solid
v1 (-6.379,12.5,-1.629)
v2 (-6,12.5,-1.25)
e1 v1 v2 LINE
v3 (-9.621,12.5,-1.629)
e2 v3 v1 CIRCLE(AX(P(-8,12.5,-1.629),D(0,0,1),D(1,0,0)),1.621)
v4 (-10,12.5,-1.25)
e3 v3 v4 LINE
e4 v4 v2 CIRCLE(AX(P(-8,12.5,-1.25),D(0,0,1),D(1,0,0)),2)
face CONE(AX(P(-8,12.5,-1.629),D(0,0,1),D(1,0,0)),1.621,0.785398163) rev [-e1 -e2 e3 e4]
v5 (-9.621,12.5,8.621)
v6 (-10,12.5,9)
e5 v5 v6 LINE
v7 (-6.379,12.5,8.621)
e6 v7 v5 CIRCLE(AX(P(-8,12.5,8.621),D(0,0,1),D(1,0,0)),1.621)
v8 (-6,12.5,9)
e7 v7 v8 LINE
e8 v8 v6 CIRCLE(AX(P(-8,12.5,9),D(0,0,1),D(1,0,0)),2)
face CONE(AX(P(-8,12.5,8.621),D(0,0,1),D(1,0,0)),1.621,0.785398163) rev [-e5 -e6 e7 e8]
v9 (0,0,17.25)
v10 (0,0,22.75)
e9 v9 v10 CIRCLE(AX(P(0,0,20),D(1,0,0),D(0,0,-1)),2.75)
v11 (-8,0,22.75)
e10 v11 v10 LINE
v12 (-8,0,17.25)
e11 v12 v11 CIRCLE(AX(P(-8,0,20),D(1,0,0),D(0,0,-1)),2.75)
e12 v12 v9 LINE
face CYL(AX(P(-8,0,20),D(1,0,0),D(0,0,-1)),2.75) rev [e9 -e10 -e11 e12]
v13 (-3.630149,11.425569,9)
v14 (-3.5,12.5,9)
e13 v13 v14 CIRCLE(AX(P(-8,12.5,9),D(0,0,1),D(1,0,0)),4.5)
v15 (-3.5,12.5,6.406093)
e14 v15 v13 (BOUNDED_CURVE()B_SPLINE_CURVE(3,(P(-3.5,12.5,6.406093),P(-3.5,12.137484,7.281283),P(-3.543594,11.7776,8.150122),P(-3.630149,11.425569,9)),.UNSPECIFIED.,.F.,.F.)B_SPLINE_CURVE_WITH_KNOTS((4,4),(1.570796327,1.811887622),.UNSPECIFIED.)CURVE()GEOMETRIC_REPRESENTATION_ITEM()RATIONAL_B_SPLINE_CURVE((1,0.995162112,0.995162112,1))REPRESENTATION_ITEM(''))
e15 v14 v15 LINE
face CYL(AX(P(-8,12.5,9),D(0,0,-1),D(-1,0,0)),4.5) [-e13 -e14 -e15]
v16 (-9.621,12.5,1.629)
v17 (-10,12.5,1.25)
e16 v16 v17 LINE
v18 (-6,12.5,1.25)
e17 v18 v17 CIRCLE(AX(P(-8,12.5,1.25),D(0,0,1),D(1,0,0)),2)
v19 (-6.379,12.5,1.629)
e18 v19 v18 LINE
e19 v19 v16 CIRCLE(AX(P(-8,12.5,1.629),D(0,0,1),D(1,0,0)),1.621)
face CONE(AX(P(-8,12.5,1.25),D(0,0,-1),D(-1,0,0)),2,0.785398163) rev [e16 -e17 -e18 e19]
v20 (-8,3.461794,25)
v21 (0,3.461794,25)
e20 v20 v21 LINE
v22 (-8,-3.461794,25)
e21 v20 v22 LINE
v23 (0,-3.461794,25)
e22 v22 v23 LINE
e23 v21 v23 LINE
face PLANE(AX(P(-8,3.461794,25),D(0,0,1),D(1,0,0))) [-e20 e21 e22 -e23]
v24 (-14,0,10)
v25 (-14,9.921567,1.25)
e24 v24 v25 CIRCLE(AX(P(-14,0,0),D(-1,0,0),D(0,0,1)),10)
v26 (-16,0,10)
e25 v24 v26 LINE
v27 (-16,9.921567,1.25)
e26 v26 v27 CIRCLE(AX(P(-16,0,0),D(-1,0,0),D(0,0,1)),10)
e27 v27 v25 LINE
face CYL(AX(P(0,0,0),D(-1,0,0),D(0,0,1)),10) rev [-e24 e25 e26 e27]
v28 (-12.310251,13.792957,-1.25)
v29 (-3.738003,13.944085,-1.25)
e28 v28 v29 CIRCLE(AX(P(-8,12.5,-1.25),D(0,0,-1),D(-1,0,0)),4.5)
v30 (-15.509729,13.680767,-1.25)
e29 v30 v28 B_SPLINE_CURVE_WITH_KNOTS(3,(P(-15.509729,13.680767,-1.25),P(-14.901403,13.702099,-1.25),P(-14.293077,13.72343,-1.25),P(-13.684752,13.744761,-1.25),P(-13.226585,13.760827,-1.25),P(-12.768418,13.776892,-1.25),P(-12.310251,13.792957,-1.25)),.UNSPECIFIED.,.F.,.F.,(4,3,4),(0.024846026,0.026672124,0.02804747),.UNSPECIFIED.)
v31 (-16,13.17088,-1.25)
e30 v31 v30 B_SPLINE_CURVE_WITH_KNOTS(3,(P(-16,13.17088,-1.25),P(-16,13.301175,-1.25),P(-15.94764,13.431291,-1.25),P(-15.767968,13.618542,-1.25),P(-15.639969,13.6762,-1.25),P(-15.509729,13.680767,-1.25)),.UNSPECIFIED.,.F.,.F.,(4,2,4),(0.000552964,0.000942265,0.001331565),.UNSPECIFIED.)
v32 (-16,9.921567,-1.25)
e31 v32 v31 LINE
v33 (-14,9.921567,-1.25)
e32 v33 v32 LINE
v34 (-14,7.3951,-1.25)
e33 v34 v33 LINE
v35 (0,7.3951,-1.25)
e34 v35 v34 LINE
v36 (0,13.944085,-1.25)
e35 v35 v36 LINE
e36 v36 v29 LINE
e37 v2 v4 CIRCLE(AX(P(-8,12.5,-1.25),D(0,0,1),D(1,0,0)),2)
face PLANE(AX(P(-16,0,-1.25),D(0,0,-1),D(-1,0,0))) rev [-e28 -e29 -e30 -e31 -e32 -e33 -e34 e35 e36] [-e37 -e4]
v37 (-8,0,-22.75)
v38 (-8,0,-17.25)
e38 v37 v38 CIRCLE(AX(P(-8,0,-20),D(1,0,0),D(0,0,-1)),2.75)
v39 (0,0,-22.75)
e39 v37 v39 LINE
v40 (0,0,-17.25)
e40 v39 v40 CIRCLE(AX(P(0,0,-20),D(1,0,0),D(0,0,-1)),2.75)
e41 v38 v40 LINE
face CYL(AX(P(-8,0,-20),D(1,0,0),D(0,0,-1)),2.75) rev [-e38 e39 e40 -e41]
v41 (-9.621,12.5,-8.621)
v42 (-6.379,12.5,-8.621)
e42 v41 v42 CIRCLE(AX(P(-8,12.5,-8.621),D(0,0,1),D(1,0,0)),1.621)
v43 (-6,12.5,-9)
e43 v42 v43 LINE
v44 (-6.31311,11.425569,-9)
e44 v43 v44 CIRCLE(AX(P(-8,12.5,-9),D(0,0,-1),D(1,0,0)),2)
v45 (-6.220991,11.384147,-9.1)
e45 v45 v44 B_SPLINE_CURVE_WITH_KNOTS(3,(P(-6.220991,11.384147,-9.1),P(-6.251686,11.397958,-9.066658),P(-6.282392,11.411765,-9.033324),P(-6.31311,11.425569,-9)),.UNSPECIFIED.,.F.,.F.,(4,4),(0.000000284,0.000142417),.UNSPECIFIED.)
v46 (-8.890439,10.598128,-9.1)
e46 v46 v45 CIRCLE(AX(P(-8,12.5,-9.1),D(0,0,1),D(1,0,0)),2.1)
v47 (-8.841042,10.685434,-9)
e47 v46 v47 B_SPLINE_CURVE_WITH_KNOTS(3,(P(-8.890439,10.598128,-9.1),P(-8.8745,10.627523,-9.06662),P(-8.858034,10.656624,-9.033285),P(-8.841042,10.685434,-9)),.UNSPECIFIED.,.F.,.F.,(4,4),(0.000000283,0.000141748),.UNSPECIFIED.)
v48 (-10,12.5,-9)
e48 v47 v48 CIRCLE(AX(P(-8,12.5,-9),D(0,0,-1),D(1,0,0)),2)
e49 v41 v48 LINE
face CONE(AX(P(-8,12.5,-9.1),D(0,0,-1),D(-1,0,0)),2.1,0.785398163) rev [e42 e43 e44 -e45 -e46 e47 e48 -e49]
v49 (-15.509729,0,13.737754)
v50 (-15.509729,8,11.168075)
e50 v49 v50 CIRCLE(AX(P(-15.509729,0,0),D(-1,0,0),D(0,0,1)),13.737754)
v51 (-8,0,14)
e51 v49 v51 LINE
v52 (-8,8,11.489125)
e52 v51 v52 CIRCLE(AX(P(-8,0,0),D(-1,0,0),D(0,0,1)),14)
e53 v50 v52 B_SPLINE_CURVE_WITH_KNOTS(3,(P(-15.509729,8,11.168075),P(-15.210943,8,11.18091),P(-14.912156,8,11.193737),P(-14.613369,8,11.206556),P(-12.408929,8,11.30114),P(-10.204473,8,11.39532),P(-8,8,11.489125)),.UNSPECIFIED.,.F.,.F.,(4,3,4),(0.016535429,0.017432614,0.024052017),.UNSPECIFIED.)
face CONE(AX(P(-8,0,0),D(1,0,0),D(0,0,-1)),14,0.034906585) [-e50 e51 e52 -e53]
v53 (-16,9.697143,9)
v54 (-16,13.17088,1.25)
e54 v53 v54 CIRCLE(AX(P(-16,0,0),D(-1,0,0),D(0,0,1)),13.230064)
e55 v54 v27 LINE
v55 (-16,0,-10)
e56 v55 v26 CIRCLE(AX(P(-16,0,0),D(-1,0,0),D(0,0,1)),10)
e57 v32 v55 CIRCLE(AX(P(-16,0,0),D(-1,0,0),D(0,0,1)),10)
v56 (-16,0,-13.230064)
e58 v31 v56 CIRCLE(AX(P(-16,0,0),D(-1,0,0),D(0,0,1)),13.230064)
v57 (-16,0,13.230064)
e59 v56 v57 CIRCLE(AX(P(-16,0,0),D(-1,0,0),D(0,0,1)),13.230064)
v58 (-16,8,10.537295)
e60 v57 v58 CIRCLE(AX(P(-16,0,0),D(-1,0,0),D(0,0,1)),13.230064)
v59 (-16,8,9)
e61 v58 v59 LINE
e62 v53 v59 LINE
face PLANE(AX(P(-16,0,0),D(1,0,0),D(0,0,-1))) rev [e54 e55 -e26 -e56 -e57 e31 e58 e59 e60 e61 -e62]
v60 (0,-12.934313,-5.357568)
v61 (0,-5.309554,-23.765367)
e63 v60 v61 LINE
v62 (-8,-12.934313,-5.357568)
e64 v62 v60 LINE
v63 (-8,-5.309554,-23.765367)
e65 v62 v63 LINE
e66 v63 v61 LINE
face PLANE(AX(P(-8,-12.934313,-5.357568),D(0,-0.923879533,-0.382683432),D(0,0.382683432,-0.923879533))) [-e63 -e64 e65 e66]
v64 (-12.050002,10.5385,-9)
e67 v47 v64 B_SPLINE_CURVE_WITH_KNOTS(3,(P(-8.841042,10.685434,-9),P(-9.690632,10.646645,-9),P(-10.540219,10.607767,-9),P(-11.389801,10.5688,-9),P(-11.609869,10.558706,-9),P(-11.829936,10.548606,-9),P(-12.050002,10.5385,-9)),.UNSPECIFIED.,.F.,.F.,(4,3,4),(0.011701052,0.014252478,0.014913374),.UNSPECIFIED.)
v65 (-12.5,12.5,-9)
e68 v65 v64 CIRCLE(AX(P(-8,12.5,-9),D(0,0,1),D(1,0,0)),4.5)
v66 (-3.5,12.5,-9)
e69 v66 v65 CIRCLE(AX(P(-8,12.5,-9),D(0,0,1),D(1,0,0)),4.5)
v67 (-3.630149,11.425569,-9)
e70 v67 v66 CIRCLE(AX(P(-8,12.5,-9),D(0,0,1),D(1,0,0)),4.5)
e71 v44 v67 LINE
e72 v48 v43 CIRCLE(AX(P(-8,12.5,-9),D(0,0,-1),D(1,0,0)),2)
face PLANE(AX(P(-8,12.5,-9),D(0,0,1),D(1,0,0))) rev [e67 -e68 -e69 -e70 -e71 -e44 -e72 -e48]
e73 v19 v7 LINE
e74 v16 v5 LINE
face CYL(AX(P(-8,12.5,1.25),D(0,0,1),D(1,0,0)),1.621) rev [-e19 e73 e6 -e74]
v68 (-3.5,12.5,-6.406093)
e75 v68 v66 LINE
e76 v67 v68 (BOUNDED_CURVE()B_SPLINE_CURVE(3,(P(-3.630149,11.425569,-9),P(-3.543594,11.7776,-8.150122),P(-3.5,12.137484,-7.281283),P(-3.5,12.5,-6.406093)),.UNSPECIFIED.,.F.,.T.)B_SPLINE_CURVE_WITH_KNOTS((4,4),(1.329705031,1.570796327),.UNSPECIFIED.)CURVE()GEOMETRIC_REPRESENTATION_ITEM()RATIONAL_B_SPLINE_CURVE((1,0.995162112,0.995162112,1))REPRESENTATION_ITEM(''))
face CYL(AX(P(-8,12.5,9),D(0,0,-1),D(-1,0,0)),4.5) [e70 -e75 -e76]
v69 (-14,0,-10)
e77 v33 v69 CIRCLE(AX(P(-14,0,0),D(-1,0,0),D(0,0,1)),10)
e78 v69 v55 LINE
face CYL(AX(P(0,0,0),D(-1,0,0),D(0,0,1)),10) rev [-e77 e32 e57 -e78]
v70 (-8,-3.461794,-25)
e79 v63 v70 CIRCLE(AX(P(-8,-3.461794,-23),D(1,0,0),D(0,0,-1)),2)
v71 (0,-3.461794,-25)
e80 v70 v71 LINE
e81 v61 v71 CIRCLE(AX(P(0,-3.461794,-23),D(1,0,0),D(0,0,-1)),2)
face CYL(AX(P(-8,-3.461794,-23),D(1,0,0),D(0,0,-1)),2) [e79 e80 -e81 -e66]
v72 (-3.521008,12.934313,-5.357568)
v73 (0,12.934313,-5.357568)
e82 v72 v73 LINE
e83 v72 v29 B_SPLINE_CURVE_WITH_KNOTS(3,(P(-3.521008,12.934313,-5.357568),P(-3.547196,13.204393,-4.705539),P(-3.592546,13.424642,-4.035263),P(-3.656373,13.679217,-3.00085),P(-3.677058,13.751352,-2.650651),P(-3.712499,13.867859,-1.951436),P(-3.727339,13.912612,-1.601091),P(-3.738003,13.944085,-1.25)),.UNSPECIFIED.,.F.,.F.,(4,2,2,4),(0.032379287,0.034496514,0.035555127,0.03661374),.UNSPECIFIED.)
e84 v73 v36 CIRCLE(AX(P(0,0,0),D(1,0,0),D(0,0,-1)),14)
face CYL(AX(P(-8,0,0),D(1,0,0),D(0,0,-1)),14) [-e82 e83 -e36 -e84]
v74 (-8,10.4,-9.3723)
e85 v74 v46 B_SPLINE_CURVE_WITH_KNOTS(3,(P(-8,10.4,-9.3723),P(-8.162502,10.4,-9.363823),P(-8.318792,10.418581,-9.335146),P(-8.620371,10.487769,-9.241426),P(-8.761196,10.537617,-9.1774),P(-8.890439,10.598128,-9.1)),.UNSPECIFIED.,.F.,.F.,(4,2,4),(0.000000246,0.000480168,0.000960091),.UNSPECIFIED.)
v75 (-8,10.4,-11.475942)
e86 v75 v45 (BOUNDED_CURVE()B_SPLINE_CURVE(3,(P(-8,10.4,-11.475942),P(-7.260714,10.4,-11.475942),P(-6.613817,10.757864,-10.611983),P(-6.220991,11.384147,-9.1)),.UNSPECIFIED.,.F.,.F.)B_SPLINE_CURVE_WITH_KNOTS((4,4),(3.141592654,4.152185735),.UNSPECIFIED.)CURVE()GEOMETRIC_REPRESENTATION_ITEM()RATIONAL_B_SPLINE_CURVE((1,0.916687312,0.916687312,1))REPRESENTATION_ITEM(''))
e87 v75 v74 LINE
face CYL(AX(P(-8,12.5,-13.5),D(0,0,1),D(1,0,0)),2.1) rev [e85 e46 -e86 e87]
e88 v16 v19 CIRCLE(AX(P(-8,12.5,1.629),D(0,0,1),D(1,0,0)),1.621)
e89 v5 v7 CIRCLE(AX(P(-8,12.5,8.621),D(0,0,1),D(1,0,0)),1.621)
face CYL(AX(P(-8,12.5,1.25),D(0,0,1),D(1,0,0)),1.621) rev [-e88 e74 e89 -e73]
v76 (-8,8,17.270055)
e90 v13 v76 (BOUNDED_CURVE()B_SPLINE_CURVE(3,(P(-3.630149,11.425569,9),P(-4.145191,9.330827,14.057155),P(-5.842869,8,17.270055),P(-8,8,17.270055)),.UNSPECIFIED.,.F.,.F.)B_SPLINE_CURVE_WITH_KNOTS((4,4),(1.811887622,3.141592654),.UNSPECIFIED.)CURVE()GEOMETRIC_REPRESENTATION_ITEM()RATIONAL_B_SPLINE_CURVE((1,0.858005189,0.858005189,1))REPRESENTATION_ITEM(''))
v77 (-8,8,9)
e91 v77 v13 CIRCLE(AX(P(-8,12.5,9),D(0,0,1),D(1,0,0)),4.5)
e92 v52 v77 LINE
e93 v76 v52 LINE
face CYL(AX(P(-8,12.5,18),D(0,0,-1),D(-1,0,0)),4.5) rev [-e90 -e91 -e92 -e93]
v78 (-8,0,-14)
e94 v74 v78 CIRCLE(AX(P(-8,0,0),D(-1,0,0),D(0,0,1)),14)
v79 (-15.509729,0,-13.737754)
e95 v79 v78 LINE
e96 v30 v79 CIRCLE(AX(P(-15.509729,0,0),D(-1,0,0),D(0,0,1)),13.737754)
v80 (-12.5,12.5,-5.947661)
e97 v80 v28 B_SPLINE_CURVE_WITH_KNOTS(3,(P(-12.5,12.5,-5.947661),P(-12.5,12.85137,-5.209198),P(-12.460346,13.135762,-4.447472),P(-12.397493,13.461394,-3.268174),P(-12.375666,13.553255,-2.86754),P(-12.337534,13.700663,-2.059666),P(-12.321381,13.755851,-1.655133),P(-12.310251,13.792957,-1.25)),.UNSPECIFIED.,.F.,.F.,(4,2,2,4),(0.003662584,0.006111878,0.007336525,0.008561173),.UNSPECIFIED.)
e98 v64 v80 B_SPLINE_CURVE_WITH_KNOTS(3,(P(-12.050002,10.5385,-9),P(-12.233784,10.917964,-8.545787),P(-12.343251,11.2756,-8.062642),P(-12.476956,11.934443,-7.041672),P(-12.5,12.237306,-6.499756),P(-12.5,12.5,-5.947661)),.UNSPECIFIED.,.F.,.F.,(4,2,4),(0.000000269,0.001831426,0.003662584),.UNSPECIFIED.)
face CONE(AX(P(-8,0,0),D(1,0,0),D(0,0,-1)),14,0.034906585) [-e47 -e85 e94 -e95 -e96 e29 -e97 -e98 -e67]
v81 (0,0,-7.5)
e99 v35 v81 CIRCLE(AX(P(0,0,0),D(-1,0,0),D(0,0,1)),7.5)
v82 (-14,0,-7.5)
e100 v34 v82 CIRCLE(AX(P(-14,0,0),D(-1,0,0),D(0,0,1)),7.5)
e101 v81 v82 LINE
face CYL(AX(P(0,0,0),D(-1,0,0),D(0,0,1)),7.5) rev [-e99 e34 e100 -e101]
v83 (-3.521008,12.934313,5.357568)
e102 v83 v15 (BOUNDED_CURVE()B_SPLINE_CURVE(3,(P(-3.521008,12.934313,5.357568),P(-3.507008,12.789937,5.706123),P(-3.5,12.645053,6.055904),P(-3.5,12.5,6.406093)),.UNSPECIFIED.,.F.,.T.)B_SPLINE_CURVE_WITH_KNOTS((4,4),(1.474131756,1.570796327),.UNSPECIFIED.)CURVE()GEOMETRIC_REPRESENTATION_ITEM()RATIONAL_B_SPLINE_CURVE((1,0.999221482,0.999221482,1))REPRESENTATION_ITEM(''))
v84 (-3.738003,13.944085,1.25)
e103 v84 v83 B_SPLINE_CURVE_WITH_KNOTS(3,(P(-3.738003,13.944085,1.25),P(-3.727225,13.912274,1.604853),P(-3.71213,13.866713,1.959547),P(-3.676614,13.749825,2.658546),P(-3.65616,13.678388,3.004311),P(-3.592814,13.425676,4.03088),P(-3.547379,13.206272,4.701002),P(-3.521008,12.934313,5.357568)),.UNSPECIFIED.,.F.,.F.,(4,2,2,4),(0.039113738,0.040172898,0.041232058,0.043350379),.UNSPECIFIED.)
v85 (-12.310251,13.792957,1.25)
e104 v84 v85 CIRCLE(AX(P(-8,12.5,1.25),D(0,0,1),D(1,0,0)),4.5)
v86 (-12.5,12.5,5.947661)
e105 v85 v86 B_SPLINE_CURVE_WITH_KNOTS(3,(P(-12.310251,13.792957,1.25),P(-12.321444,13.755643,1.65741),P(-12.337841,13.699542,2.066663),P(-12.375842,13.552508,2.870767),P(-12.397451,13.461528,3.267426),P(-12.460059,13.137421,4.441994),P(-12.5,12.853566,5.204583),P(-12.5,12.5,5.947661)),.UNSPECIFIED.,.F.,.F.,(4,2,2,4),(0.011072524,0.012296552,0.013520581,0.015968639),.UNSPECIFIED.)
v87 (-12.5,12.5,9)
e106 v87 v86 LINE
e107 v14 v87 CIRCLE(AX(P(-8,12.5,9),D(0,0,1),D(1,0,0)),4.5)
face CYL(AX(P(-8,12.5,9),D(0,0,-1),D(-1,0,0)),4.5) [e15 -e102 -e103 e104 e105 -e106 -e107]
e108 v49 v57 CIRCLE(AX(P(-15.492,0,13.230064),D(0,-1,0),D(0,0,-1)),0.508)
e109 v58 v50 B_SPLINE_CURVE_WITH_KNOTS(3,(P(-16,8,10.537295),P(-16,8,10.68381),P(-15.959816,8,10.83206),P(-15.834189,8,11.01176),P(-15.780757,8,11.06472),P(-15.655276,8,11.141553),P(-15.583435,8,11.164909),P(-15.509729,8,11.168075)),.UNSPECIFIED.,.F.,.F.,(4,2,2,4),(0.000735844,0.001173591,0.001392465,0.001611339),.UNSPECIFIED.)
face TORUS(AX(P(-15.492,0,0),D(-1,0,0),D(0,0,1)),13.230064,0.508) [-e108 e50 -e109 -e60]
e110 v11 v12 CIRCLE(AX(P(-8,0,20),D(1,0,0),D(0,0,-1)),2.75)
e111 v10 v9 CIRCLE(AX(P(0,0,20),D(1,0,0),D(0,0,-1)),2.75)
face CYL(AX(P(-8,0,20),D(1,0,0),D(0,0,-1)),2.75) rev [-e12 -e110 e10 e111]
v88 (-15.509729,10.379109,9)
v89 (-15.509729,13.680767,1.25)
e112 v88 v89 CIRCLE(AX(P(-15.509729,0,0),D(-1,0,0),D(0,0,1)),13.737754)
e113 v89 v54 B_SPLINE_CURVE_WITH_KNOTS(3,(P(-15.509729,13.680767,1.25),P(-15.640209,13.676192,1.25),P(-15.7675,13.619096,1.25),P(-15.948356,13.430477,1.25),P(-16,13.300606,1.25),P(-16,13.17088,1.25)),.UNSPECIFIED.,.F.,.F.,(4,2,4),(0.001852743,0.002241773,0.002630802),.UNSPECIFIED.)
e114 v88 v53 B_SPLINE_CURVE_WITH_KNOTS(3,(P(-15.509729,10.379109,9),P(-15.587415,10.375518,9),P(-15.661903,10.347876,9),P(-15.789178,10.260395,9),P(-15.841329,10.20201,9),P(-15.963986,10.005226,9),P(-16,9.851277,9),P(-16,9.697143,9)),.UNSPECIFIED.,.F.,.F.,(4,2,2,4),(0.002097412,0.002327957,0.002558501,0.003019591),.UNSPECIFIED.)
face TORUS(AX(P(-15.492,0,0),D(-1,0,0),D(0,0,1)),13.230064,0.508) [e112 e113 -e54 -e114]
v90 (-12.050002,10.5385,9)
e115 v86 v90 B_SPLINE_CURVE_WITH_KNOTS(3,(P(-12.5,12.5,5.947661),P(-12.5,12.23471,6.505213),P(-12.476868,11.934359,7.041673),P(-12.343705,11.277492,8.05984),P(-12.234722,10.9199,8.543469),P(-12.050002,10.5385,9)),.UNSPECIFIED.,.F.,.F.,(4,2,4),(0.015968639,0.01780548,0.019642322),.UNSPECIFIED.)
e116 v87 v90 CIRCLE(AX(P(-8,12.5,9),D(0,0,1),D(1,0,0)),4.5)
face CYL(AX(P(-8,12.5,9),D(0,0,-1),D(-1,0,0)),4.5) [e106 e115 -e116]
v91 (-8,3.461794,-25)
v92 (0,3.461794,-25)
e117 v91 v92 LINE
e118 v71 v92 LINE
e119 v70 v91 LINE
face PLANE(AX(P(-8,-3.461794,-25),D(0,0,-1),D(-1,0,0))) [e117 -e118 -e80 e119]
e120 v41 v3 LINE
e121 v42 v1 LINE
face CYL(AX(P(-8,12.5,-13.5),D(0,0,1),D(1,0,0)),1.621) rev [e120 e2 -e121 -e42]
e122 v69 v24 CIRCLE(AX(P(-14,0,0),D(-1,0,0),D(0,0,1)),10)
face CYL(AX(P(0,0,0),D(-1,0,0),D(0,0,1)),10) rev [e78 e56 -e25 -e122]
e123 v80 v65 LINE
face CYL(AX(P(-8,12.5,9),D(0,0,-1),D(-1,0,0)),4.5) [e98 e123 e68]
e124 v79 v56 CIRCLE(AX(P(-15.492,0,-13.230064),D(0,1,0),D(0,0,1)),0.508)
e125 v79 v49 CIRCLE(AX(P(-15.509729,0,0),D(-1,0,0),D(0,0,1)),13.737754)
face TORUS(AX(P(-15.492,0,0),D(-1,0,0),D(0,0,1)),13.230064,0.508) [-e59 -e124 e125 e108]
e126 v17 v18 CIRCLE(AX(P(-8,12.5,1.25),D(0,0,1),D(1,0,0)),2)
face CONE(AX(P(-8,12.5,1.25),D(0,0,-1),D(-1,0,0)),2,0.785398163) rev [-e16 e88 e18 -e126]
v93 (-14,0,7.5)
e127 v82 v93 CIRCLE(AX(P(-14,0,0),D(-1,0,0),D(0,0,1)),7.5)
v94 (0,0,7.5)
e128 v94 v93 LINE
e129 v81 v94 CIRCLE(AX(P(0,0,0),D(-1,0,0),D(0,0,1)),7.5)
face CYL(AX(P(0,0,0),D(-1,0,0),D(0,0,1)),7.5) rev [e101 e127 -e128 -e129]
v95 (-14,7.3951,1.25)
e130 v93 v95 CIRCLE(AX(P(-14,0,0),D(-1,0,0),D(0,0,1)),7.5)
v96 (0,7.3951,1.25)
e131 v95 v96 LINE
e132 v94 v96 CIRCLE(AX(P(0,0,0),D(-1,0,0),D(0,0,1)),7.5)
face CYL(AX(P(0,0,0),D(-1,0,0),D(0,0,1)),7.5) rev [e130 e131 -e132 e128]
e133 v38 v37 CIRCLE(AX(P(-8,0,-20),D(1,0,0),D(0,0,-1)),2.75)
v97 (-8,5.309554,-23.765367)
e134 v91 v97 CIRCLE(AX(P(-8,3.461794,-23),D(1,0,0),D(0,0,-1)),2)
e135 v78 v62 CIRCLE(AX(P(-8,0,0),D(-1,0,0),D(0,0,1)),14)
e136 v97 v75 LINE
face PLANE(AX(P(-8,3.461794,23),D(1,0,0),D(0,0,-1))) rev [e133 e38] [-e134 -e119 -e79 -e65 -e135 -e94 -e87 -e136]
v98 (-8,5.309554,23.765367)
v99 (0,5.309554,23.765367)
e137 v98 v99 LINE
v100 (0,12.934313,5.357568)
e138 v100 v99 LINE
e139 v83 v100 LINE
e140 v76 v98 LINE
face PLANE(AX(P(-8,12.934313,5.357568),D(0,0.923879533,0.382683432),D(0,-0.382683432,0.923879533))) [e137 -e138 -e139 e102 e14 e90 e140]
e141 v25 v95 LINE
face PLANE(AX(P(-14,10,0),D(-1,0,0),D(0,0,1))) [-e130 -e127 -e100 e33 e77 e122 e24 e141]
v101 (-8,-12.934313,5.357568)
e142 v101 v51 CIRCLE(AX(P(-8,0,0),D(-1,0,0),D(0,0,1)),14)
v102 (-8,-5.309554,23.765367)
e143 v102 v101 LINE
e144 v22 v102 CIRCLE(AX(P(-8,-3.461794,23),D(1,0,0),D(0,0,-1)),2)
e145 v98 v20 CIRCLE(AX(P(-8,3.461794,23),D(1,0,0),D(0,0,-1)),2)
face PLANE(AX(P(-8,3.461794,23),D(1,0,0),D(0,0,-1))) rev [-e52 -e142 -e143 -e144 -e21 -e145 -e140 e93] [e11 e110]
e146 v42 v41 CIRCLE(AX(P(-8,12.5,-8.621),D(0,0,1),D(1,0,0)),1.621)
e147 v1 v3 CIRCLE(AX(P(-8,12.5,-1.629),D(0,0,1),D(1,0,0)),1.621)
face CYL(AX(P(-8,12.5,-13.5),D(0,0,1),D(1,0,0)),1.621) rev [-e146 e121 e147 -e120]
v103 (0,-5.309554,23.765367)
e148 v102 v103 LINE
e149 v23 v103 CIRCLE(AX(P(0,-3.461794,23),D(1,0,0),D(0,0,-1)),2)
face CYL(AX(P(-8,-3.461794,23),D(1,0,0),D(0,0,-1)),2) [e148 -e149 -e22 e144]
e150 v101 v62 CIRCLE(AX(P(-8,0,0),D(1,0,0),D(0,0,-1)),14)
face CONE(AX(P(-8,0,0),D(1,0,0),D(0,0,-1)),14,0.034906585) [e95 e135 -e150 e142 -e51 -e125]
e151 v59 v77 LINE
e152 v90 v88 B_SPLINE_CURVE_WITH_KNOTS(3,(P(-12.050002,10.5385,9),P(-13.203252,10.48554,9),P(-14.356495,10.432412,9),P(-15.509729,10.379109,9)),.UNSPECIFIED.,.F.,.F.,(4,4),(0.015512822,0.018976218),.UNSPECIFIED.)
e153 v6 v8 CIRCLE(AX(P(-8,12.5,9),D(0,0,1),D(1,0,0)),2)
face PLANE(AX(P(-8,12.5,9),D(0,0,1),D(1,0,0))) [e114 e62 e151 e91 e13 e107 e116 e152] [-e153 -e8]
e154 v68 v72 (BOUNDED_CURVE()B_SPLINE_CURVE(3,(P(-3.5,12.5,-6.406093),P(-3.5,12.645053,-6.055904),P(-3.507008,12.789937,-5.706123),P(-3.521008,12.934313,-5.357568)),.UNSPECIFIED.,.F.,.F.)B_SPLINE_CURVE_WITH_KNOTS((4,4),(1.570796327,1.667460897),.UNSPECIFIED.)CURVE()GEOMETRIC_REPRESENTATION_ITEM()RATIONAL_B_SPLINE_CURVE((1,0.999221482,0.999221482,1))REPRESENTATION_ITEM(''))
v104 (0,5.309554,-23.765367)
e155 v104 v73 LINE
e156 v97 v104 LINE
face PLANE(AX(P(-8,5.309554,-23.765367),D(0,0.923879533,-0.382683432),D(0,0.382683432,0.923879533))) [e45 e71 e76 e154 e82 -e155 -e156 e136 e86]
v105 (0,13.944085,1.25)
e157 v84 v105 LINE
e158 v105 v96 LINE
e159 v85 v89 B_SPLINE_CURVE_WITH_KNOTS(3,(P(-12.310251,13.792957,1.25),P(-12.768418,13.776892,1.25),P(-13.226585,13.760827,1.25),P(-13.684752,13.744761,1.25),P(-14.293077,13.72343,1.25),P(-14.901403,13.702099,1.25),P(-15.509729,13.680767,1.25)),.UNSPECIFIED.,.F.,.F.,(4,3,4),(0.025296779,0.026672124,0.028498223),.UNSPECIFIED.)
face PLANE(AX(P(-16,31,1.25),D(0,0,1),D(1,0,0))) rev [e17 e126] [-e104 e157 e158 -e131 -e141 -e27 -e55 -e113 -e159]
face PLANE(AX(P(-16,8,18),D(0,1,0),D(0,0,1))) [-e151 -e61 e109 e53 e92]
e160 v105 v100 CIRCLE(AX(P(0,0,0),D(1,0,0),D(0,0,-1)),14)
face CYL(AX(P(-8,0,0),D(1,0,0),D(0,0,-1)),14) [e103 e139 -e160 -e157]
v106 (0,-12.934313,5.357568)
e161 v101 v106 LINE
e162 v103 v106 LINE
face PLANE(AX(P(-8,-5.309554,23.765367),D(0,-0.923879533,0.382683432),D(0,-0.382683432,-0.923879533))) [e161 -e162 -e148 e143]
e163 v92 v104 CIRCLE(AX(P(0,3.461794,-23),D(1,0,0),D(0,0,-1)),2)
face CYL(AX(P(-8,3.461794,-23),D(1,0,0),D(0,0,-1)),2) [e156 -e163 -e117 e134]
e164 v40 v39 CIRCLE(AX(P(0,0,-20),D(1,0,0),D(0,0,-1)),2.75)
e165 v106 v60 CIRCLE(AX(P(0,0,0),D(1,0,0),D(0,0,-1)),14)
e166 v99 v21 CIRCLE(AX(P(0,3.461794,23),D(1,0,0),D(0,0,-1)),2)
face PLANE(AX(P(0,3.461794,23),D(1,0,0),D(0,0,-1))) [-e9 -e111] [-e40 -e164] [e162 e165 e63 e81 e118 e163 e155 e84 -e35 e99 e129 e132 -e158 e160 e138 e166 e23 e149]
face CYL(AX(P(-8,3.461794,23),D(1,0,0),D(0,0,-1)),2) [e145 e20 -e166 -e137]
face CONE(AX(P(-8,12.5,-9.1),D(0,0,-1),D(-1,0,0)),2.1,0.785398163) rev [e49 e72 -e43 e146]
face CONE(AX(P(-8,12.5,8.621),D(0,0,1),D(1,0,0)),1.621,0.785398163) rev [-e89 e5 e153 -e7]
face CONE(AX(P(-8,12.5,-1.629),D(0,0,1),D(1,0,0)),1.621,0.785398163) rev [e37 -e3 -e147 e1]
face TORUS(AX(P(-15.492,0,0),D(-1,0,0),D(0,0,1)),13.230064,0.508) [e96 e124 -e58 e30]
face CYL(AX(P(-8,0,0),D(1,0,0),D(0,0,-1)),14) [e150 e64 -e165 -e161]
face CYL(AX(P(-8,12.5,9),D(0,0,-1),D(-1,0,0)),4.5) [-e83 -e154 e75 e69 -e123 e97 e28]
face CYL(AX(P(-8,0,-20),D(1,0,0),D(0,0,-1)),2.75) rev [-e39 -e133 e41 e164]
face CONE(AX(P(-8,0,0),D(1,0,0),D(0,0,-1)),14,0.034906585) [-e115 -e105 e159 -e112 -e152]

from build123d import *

# Parameters (mm, degrees)
EXTRUDE_1_DEPTH      = 8
EXTRUDE_2_DEPTH      = 9
EXTRUDE_2_DEPTH_BACK = 9
SKETCH_3_R           = 4.5
CUT_EXTRUDE_1_DEPTH  = 9
SKETCH_5_W           = 2.5
SKETCH_5_H           = 31
CUT_EXTRUDE_2_DEPTH  = 16
SKETCH_9_R           = 2.75
CUT_EXTRUDE_3_DEPTH  = 8
SKETCH_10_R          = 2.75
CUT_EXTRUDE_4_DEPTH  = 8


with BuildPart() as part:
    # 草图1 → 凸台-拉伸1 (new body)
    with BuildSketch(Plane(origin=(0, 0, 0), x_dir=(0, 0, -1), z_dir=(1, 0, 0))):
        with BuildLine():
            Line((-25, 3.461794469), (-25, -3.461794469))
            ThreePointArc((-25, -3.461794469), (-24.662939225, -4.572934935), (-23.765366865, -5.309553534))
            Line((-23.765366865, -5.309553534), (-5.357568053, -12.934313455))
            ThreePointArc((-5.357568053, -12.934313455), (-2.731264508, -13.730993926), (0, -14))
            ThreePointArc((0, -14), (2.731264508, -13.730993926), (5.357568053, -12.934313455))
            Line((5.357568053, -12.934313455), (23.765366865, -5.309553534))
            ThreePointArc((23.765366865, -5.309553534), (24.662939225, -4.572934935), (25, -3.461794469))
            Line((25, -3.461794469), (25, 3.461794469))
            ThreePointArc((25, 3.461794469), (24.662939225, 4.572934935), (23.765366865, 5.309553534))
            Line((23.765366865, 5.309553534), (5.357568053, 12.934313455))
            ThreePointArc((5.357568053, 12.934313455), (2.731264508, 13.730993926), (0, 14))
            ThreePointArc((0, 14), (-2.731264508, 13.730993926), (-5.357568053, 12.934313455))
            Line((-5.357568053, 12.934313455), (-23.765366865, 5.309553534))
            ThreePointArc((-23.765366865, 5.309553534), (-24.662939225, 4.572934935), (-25, 3.461794469))
        make_face()
    extrude(amount=-EXTRUDE_1_DEPTH)

    # 草图2 → 旋转1 (revolve)
    with BuildSketch(Plane.XY, mode=Mode.PRIVATE) as revolve_1_sk:
        with BuildLine():
            Line((-16, 0), (-16, 13.230063946))
            ThreePointArc((-16, 13.230063946), (-15.857424619, 13.582950399), (-15.509728944, 13.737754487))
            Line((-15.509728944, 13.737754487), (-8, 14))
            Line((-8, 14), (-8, 0))
            Line((-8, 0), (-16, 0))
        make_face()
    revolve(revolve_1_sk.sketch.rotate(Axis((-8, 0, 0), (-1, 0, 0)), 270), axis=Axis((-8, 0, 0), (-1, 0, 0)))

    # 草图3 → 凸台-拉伸2 (add, two sides: drawn at the far end of the back side and taken through both)
    with BuildSketch(Plane.XY.offset(-EXTRUDE_2_DEPTH_BACK)):
        with Locations((-8, 12.5)):
            Circle(SKETCH_3_R)
    extrude(amount=EXTRUDE_2_DEPTH + EXTRUDE_2_DEPTH_BACK)

    # 草图4 → 切除-拉伸1 (cut)
    with BuildSketch(Plane.XY.offset(9)):
        with BuildLine():
            Line((-16, 8), (-8, 8))
            ThreePointArc((-8, 8), (-4.818019485, 15.681980515), (-12.5, 12.5))
            Line((-12.5, 12.5), (-16, 12.5))
            Line((-16, 12.5), (-16, 8))
        make_face()
    extrude(amount=CUT_EXTRUDE_1_DEPTH, mode=Mode.SUBTRACT)

    # 草图5 → 切除-拉伸2 (cut)
    with BuildSketch(Plane(origin=(0, 0, 0), x_dir=(0, 0, -1), z_dir=(1, 0, 0))):
        with Locations((0, 15.5)):
            Rectangle(SKETCH_5_W, SKETCH_5_H)
    extrude(amount=-CUT_EXTRUDE_2_DEPTH, mode=Mode.SUBTRACT)

    # 草图6 → 切除-旋转1 (revolve, cut)
    with BuildSketch(Plane.XY):
        Polygon((-16, 0), (-16, 10), (-14, 10), (-14, 7.5), (0, 7.5), (0, 0), align=None)
    revolve(axis=Axis((0, 0, 0), (-1, 0, 0)), mode=Mode.SUBTRACT)

    # 草图7 → 切除-旋转2 (revolve, cut)
    with BuildSketch(Plane(origin=(-8, 0, 0), x_dir=(0, 0, -1), z_dir=(1, 0, 0)), mode=Mode.PRIVATE) as cut_revolve_2_sk:
        Polygon((1.25, 12.5), (1.25, 14.5), (1.629, 14.121), (8.621, 14.121), (9.1, 14.6), (13.5, 14.6), (13.5, 12.5), align=None)
    revolve(cut_revolve_2_sk.sketch.rotate(Axis((-8, 12.5, -13.5), (0, 0, 1)), 270), axis=Axis((-8, 12.5, -13.5), (0, 0, 1)), mode=Mode.SUBTRACT)

    # 草图8 → 切除-旋转3 (revolve, cut)
    with BuildSketch(Plane(origin=(-8, 0, 0), x_dir=(0, 0, -1), z_dir=(1, 0, 0)), mode=Mode.PRIVATE) as cut_revolve_3_sk:
        Polygon((-9, 12.5), (-9, 14.5), (-8.621, 14.121), (-1.629, 14.121), (-1.25, 14.5), (-1.25, 12.5), align=None)
    revolve(cut_revolve_3_sk.sketch.rotate(Axis((-8, 12.5, 1.25), (0, 0, 1)), 270), axis=Axis((-8, 12.5, 1.25), (0, 0, 1)), mode=Mode.SUBTRACT)

    # 草图9 → 切除-拉伸3 (cut)
    with BuildSketch(Plane(origin=(0, 0, 0), x_dir=(0, 0, -1), z_dir=(1, 0, 0))):
        with Locations((20, 0)):
            Circle(SKETCH_9_R)
    extrude(amount=-CUT_EXTRUDE_3_DEPTH, mode=Mode.SUBTRACT)

    # 草图10 → 切除-拉伸4 (cut)
    with BuildSketch(Plane(origin=(0, 0, 0), x_dir=(0, 0, -1), z_dir=(1, 0, 0))):
        with Locations((-20, 0)):
            Circle(SKETCH_10_R)
    extrude(amount=-CUT_EXTRUDE_4_DEPTH, mode=Mode.SUBTRACT)


solid = part.part
